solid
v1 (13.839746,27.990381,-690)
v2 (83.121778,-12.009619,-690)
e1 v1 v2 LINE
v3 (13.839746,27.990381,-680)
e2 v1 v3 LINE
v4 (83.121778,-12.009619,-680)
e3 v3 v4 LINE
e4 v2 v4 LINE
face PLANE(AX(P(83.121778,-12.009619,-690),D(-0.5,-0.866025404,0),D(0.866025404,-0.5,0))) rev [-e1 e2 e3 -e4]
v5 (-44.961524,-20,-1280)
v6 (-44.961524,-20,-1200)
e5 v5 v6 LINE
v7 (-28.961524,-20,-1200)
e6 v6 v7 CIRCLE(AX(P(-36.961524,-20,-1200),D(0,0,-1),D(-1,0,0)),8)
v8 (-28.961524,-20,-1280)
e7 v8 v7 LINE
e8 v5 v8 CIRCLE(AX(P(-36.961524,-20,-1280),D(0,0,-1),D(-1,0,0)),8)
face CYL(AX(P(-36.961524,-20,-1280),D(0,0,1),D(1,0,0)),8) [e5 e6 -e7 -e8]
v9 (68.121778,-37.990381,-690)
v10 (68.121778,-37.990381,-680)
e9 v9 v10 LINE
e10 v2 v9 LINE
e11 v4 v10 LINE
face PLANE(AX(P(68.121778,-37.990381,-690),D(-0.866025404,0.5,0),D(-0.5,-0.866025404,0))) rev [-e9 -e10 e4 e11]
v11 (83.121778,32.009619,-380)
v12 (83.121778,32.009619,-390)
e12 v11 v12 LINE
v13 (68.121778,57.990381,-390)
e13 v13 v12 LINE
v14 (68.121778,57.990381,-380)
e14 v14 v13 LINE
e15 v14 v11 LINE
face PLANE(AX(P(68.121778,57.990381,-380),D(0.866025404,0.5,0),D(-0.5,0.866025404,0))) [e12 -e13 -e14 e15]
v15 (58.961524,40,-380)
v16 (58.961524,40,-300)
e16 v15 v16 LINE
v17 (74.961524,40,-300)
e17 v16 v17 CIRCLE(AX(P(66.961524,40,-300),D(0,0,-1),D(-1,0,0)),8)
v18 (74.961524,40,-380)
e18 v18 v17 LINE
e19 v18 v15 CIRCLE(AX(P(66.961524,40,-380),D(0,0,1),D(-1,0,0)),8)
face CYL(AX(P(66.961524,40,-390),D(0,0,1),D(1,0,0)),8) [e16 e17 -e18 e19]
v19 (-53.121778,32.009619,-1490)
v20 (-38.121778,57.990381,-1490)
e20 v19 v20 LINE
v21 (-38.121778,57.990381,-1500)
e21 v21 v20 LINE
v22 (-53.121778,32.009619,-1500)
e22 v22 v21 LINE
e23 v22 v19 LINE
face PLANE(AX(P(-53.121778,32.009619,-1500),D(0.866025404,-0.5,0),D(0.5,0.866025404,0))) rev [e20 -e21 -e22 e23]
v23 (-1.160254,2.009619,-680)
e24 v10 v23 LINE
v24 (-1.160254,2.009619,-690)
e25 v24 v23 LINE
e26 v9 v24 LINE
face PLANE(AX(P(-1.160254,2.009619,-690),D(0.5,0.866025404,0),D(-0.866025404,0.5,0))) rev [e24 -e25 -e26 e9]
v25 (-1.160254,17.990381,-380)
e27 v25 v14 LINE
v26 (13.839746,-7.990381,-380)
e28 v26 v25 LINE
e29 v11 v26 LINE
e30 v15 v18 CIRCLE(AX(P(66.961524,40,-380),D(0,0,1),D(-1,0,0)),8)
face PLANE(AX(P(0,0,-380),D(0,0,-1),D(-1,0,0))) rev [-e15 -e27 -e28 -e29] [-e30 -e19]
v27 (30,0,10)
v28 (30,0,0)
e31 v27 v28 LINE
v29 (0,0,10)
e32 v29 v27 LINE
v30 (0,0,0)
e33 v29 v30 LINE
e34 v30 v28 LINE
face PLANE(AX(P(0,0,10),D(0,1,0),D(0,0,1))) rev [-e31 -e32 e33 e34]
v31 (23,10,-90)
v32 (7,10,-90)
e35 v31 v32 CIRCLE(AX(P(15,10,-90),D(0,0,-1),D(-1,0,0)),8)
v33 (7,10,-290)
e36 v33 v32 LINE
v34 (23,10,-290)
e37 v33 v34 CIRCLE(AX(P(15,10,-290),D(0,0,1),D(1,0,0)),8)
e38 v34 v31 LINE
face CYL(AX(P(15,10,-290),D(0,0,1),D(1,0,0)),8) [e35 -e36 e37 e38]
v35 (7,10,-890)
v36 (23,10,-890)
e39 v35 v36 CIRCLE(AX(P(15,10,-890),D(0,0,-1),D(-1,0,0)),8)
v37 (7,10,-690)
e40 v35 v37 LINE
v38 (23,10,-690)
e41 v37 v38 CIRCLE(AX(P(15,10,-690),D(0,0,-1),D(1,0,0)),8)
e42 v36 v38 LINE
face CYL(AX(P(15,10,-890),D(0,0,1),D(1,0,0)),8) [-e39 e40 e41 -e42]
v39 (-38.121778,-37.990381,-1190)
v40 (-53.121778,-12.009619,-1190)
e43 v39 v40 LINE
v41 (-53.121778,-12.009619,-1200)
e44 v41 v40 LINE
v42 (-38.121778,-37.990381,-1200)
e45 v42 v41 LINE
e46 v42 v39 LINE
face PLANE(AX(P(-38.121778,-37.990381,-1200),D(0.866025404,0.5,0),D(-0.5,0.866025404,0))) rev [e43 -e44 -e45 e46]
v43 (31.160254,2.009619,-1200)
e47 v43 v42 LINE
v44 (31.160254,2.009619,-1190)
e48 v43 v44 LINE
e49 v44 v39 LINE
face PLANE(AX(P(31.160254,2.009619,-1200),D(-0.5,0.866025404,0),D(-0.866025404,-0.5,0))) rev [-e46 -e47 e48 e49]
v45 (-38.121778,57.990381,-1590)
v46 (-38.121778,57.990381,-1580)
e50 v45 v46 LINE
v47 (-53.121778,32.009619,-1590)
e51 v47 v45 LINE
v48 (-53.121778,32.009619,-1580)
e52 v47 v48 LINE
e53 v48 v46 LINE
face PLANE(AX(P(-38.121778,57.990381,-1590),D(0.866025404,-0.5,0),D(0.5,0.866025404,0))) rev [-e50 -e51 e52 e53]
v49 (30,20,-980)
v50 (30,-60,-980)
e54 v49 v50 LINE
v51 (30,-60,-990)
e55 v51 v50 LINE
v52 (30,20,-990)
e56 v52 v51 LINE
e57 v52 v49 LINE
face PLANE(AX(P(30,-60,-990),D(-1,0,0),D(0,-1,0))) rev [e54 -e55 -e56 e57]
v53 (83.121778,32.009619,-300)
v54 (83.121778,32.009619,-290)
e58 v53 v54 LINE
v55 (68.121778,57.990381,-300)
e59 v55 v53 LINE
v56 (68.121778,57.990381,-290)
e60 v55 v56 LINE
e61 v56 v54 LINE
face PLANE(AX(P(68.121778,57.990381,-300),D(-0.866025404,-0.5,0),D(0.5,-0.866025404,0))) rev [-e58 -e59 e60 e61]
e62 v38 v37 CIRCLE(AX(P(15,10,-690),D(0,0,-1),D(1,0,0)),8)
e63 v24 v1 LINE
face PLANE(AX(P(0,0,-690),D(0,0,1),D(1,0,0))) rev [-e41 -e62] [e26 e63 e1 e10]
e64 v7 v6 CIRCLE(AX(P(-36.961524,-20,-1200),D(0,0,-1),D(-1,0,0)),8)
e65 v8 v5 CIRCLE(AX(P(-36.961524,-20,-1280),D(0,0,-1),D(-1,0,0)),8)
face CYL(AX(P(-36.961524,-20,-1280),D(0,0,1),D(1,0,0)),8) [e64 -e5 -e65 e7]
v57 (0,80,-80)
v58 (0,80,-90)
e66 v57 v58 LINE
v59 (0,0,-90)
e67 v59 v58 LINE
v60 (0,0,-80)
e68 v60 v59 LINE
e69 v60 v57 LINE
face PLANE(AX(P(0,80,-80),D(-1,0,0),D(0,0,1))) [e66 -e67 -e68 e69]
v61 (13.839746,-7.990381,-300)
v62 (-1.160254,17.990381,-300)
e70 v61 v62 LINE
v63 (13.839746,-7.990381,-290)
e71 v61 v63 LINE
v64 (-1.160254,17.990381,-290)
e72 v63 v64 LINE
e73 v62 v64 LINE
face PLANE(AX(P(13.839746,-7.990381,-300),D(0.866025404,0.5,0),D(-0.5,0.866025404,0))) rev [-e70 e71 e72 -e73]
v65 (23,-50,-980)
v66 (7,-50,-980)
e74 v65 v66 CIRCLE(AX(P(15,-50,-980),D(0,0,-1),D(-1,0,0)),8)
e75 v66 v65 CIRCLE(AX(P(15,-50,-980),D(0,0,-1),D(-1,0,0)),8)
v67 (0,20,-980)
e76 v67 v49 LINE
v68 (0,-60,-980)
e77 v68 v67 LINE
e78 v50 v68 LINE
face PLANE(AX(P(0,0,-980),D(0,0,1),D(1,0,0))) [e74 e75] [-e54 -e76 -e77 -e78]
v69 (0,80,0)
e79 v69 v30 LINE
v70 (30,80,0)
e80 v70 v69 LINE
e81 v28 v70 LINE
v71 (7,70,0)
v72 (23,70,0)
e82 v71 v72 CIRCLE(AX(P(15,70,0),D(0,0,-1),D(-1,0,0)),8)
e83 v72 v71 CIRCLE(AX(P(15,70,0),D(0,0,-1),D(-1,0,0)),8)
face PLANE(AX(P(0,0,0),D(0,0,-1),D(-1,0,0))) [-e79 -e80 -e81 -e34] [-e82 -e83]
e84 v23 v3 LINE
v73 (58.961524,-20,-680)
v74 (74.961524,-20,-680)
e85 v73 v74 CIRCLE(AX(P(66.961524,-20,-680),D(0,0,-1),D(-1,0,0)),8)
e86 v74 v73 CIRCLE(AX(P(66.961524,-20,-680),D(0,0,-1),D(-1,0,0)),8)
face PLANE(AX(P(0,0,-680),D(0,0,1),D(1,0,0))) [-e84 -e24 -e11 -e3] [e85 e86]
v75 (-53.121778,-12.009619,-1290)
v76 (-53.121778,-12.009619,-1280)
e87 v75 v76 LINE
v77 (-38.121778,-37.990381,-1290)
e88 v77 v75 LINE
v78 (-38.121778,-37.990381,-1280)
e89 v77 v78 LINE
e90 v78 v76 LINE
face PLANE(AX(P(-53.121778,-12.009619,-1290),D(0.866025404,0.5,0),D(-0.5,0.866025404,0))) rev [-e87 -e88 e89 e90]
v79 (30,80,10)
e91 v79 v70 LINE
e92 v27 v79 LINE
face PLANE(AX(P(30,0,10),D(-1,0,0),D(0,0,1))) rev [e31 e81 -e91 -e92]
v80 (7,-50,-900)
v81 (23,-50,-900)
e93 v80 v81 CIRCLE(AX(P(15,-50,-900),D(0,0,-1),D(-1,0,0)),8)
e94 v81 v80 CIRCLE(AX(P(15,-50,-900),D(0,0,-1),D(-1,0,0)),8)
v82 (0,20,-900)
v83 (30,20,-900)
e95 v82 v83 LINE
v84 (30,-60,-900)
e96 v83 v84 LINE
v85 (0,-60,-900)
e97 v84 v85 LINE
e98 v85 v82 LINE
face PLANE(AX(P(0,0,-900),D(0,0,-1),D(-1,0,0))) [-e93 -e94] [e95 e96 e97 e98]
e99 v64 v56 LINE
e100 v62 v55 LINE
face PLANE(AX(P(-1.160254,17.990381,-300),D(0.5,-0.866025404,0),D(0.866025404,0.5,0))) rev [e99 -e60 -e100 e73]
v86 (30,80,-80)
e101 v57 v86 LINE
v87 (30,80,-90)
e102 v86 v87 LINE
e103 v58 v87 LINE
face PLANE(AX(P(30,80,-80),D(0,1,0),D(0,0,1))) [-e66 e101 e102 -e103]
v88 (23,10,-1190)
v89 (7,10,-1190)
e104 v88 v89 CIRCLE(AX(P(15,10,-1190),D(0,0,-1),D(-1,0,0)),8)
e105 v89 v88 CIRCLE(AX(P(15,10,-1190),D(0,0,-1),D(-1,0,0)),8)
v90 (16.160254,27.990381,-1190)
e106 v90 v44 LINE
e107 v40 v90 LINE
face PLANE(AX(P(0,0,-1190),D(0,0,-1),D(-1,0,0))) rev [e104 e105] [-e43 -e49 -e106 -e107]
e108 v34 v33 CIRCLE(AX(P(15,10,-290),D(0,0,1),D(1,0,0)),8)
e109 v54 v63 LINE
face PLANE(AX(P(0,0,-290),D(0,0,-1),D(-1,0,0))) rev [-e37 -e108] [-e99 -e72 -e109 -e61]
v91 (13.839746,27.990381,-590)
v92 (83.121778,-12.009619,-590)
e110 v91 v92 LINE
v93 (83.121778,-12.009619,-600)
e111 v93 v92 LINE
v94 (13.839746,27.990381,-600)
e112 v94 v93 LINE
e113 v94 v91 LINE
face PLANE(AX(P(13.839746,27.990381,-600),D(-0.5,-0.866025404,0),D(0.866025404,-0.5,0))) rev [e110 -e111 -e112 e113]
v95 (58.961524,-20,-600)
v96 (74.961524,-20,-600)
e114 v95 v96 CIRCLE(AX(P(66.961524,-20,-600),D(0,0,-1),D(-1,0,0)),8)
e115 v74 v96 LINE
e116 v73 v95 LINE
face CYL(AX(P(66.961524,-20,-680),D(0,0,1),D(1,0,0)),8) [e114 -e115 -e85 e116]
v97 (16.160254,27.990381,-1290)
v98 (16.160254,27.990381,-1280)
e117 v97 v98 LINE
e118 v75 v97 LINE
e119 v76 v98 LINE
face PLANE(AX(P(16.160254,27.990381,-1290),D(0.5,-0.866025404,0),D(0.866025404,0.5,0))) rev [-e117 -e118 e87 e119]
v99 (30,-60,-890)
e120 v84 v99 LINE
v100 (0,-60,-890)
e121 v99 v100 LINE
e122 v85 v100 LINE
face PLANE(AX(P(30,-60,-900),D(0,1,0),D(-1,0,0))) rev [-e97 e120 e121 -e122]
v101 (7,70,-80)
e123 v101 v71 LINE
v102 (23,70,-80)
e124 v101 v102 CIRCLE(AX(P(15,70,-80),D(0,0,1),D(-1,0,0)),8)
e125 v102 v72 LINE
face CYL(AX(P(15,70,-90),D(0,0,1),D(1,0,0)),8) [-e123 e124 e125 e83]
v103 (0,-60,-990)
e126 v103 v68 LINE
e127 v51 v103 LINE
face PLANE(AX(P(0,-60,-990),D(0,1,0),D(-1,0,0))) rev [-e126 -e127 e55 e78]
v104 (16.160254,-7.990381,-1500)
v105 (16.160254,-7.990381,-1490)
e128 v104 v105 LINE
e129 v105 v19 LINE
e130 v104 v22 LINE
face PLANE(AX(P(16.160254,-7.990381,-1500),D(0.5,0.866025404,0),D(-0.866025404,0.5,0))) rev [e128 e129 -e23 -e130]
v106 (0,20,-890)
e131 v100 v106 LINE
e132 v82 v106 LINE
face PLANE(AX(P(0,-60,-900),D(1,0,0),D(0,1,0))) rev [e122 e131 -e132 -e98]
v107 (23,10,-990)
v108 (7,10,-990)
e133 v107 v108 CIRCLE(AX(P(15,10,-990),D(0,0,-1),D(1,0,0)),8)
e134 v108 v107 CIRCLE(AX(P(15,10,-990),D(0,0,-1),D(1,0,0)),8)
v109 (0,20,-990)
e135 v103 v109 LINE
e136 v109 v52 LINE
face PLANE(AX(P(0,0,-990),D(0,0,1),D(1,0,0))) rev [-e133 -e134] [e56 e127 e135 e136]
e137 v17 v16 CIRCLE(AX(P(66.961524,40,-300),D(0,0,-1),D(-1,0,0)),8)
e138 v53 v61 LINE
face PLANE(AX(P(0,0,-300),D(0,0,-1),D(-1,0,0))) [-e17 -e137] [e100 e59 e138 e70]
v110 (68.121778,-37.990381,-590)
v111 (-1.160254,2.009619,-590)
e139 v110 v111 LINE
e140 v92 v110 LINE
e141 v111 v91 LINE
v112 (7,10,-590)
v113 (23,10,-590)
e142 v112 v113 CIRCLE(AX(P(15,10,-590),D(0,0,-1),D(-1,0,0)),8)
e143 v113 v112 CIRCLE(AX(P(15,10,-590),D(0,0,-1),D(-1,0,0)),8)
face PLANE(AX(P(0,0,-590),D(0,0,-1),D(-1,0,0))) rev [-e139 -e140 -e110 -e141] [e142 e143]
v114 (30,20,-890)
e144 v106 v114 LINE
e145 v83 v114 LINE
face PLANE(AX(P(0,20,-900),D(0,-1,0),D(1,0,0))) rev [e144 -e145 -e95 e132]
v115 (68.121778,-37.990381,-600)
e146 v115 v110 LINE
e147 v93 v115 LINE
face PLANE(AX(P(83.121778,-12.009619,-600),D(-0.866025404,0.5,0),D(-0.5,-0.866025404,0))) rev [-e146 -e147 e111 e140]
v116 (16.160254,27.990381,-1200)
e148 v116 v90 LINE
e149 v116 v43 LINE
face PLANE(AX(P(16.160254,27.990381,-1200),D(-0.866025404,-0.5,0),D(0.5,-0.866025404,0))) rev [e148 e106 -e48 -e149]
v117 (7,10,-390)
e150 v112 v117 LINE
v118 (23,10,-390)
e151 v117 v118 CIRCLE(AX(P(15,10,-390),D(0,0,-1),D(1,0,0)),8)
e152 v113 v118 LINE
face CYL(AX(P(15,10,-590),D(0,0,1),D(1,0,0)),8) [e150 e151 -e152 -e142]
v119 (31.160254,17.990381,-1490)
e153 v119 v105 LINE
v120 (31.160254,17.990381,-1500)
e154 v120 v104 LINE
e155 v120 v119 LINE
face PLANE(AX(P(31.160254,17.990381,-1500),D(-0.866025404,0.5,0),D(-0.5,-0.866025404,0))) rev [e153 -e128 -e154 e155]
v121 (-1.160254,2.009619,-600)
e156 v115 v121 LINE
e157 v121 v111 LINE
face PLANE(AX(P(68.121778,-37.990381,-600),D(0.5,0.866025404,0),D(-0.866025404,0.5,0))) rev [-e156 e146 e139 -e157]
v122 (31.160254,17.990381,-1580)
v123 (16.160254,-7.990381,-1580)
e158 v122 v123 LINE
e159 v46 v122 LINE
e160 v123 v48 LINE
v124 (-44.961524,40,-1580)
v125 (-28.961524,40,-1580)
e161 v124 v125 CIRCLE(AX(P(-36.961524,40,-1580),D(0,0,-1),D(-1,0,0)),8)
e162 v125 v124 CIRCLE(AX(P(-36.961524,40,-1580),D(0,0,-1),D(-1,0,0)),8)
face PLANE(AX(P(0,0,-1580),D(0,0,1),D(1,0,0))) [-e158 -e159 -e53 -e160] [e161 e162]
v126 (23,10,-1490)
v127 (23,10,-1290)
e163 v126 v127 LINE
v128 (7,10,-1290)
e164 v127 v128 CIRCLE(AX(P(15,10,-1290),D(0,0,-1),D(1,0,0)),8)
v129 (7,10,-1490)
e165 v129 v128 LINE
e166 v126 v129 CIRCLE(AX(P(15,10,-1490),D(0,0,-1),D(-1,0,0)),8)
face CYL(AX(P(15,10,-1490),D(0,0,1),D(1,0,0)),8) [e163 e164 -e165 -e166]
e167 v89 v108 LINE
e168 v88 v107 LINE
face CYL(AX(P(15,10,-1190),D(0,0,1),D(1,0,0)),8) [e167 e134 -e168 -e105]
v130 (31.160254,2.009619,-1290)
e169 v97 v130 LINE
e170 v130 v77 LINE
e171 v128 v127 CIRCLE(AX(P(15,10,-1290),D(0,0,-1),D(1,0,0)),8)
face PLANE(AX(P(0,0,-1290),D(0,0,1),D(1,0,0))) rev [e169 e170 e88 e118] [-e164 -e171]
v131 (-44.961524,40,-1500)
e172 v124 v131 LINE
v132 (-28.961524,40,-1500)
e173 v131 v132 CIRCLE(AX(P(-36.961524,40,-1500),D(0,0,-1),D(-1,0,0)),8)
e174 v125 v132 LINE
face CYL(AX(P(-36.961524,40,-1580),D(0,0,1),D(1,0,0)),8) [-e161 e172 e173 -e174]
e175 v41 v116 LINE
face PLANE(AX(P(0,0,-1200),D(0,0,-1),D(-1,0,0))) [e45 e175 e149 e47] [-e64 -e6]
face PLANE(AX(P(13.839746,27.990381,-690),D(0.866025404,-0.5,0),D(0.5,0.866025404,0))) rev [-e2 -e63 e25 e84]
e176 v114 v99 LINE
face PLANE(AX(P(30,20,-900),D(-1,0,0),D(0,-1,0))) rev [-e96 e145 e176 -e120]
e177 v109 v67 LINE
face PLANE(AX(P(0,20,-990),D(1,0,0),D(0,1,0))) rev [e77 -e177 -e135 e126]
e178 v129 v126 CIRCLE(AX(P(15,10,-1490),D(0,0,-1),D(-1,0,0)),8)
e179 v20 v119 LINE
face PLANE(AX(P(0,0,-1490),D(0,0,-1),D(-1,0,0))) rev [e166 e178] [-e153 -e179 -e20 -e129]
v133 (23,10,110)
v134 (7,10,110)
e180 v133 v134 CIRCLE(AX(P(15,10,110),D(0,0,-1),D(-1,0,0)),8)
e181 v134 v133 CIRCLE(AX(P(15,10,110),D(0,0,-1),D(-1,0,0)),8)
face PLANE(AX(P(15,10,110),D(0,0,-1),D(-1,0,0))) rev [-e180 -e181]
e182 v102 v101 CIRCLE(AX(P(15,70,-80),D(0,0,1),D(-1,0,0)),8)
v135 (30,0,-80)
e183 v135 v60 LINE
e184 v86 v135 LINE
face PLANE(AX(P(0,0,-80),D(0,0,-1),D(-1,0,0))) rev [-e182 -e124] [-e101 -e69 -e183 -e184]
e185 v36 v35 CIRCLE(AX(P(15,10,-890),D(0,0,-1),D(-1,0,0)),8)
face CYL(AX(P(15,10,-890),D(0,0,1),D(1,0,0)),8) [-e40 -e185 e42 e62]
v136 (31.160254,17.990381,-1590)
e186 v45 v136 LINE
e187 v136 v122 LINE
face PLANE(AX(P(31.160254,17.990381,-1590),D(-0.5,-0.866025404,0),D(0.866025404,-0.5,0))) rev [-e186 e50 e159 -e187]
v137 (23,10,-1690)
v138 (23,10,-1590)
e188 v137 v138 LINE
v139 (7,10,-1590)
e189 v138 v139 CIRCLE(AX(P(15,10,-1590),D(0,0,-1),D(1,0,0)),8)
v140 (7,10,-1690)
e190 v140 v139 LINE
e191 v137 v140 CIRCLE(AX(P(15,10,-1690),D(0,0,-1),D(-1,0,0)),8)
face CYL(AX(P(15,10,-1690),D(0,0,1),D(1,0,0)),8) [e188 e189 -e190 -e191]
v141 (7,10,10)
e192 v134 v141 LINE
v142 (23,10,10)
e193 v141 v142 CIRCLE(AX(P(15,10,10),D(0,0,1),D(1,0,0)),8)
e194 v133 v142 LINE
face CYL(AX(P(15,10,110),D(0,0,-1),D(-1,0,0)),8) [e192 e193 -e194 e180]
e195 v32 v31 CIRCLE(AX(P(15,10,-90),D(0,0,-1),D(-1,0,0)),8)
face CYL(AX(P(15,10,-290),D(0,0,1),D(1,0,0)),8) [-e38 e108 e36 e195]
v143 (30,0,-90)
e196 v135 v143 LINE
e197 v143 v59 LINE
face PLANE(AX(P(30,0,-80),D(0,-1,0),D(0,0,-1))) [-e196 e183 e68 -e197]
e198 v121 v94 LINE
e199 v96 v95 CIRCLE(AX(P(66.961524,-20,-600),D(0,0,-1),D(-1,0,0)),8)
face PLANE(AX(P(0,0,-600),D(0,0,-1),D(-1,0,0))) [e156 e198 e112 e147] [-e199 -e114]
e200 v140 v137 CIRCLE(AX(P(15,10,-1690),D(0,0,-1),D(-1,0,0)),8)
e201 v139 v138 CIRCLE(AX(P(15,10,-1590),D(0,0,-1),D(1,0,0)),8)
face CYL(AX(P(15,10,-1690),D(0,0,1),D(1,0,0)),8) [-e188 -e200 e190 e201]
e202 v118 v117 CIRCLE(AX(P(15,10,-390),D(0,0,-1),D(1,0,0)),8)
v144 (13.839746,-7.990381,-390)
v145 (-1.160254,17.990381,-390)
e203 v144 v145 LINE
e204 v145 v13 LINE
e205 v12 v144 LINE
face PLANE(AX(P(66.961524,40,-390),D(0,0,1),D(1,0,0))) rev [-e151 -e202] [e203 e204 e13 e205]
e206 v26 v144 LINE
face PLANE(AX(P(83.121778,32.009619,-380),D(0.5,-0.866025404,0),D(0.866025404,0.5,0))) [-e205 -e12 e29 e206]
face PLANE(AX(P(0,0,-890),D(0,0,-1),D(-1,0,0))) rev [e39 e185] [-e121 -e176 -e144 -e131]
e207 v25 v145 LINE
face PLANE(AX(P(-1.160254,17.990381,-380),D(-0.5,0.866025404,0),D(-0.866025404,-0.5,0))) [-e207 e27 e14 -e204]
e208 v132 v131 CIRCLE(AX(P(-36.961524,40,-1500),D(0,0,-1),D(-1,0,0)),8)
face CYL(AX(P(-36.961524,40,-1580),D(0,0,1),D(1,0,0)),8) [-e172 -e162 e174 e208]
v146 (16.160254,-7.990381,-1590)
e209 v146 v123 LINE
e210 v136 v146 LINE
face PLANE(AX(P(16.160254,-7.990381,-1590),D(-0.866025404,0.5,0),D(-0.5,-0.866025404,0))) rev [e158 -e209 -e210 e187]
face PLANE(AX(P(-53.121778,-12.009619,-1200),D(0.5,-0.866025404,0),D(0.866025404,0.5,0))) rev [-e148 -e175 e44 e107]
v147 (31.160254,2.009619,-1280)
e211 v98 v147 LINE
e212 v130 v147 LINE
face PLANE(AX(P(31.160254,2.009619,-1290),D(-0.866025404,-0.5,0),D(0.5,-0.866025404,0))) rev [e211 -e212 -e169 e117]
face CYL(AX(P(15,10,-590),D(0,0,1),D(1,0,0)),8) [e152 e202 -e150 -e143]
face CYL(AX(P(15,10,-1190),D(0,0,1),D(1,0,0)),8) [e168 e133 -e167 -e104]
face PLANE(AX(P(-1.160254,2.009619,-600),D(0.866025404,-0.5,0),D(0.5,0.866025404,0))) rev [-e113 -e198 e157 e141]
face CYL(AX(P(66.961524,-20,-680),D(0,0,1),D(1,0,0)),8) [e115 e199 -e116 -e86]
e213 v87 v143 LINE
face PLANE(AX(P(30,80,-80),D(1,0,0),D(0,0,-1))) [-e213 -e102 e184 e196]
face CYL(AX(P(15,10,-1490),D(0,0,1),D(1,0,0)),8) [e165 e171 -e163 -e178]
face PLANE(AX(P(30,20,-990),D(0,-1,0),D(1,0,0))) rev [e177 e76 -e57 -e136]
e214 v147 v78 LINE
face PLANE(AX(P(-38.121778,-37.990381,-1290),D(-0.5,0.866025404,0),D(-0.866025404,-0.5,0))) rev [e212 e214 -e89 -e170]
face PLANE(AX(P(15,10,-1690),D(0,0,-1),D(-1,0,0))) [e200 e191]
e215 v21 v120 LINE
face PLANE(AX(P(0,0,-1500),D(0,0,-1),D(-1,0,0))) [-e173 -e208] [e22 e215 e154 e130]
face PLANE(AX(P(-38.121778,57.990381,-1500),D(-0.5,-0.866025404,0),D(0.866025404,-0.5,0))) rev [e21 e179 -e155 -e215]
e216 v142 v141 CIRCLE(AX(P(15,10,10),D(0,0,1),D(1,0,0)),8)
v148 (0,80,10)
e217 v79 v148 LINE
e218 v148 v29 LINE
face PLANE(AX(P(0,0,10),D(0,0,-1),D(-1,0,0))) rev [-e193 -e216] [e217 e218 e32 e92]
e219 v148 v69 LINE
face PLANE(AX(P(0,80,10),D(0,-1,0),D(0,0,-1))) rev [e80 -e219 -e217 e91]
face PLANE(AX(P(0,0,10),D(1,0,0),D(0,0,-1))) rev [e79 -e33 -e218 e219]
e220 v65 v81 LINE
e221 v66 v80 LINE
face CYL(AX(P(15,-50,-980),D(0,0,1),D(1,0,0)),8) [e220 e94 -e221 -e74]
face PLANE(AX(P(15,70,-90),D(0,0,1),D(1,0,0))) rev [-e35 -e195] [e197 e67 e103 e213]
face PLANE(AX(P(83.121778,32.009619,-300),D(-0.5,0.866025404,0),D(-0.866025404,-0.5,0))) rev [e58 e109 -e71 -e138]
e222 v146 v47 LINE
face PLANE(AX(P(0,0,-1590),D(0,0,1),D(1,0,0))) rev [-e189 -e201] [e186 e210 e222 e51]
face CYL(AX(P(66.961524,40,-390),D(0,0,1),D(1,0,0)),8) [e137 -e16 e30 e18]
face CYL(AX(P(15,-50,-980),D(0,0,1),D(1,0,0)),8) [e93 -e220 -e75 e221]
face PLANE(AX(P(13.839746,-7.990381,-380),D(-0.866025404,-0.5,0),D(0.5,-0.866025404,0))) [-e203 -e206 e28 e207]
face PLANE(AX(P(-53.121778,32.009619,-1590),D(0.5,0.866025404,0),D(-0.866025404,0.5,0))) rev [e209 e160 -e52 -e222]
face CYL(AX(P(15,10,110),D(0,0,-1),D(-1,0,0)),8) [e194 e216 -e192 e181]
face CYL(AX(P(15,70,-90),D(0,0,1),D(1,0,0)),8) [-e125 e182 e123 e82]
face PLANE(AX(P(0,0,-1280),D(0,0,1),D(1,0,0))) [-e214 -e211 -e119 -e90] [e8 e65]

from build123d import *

# Parameters (mm, degrees)
SKETCH1_W            = 30
SKETCH1_H            = 80
SKETCH1_R            = 8
BOSS_EXTRUDE1_DEPTH  = 10
BOSS_EXTRUDE2_START  = -100
SKETCH2_R            = 8
BOSS_EXTRUDE2_DEPTH  = 100
SKETCH3_W            = 30
SKETCH3_H            = 80
SKETCH3_R            = 8
BOSS_EXTRUDE3_DEPTH  = 10
BOSS_EXTRUDE4_START  = -210
SKETCH4_R            = 8
BOSS_EXTRUDE4_DEPTH  = 210
SKETCH5_R            = 8
BOSS_EXTRUDE5_DEPTH  = 10
SKETCH6_R            = 8
BOSS_EXTRUDE6_DEPTH  = 100
BOSS_EXTRUDE7_DEPTH  = 10
BOSS_EXTRUDE8_START  = 200
SKETCH8_R            = 8
BOSS_EXTRUDE8_DEPTH  = 200
BOSS_EXTRUDE9_DEPTH  = 10
SKETCH10_R           = 8
BOSS_EXTRUDE10_DEPTH = 80
BOSS_EXTRUDE11_DEPTH = 10
BOSS_EXTRUDE12_START = 200
SKETCH12_R           = 8
BOSS_EXTRUDE12_DEPTH = 200
SKETCH13_W           = 30
SKETCH13_H           = 80
BOSS_EXTRUDE13_DEPTH = 10
SKETCH14_R           = 8
BOSS_EXTRUDE14_DEPTH = 80
SKETCH15_W           = 30
SKETCH15_H           = 80
BOSS_EXTRUDE15_DEPTH = 10
BOSS_EXTRUDE16_START = 200
SKETCH16_R           = 8
BOSS_EXTRUDE16_DEPTH = 200
BOSS_EXTRUDE17_DEPTH = 10
SKETCH18_R           = 8
BOSS_EXTRUDE18_DEPTH = 80
BOSS_EXTRUDE19_DEPTH = 10
BOSS_EXTRUDE20_START = 200
SKETCH20_R           = 8
BOSS_EXTRUDE20_DEPTH = 200
BOSS_EXTRUDE21_DEPTH = 10
SKETCH22_R           = 8
BOSS_EXTRUDE22_DEPTH = 80
BOSS_EXTRUDE23_DEPTH = 10
BOSS_EXTRUDE24_START = 100
SKETCH24_R           = 8
BOSS_EXTRUDE24_DEPTH = 100
SKETCH25_R           = 8
BOSS_EXTRUDE25_DEPTH = 110


with BuildPart() as part:
    # Sketch1 → Boss-Extrude1 (new body)
    with BuildSketch(Plane.XY):
        with Locations((15, 40)):
            Rectangle(SKETCH1_W, SKETCH1_H)
        with Locations((15, 70)):
            Circle(SKETCH1_R, mode=Mode.SUBTRACT)
        with Locations((15, 10)):
            Circle(SKETCH1_R, mode=Mode.SUBTRACT)
    extrude(amount=BOSS_EXTRUDE1_DEPTH)

    # Sketch2 → Boss-Extrude2 (add)
    with BuildSketch(Plane.XY.offset(10).offset(BOSS_EXTRUDE2_START)):
        with Locations((15, 70)):
            Circle(SKETCH2_R)
    extrude(amount=BOSS_EXTRUDE2_DEPTH)

    # Sketch3 → Boss-Extrude3 (add)
    with BuildSketch(Plane(origin=(0, 0, -90), x_dir=(-1, 0, 0), z_dir=(0, 0, -1))):
        with Locations((-15, 40)):
            Rectangle(SKETCH3_W, SKETCH3_H)
        with Locations(Location((-15, 10, 0), (0, 0, 180))):
            Circle(SKETCH3_R, mode=Mode.SUBTRACT)
    extrude(amount=-BOSS_EXTRUDE3_DEPTH)

    # Sketch4 → Boss-Extrude4 (add)
    with BuildSketch(Plane.XY.offset(-80).offset(BOSS_EXTRUDE4_START)):
        with Locations((15, 10)):
            Circle(SKETCH4_R)
    extrude(amount=BOSS_EXTRUDE4_DEPTH)

    # Sketch5 → Boss-Extrude5 (add)
    with BuildSketch(Plane(origin=(0, 0, -290), x_dir=(-1, 0, 0), z_dir=(0, 0, -1))):
        Polygon((-83.121778265, 32.009618943), (-13.839745962, -7.990381057), (1.160254038, 17.990381057), (-68.121778265, 57.990381057), align=None)
        with Locations((-66.961524227, 40)):
            Circle(SKETCH5_R, mode=Mode.SUBTRACT)
    extrude(amount=BOSS_EXTRUDE5_DEPTH)

    # Sketch6 → Boss-Extrude6 (add)
    with BuildSketch(Plane.XY.offset(-290)):
        with Locations((66.961524227, 40)):
            Circle(SKETCH6_R)
    extrude(amount=-BOSS_EXTRUDE6_DEPTH)

    # Sketch7 → Boss-Extrude7 (add)
    with BuildSketch(Plane(origin=(0, 0, -390), x_dir=(-1, 0, 0), z_dir=(0, 0, -1))):
        Polygon((-83.121778265, 32.009618943), (-13.839745962, -7.990381057), (1.160254038, 17.990381057), (-68.121778265, 57.990381057), align=None)
    extrude(amount=-BOSS_EXTRUDE7_DEPTH)

    # Sketch8 → Boss-Extrude8 (add)
    with BuildSketch(Plane(origin=(0, 0, -390), x_dir=(-1, 0, 0), z_dir=(0, 0, -1)).offset(BOSS_EXTRUDE8_START)):
        with Locations(Location((-15, 10, 0), (0, 0, 180))):
            Circle(SKETCH8_R)
    extrude(amount=-BOSS_EXTRUDE8_DEPTH)

    # Sketch9 → Boss-Extrude9 (add)
    with BuildSketch(Plane(origin=(0, 0, -590), x_dir=(-1, 0, 0), z_dir=(0, 0, -1))):
        Polygon((-68.121778265, -37.990381057), (1.160254038, 2.009618943), (-13.839745962, 27.990381057), (-83.121778265, -12.009618943), align=None)
    extrude(amount=BOSS_EXTRUDE9_DEPTH)

    # Sketch10 → Boss-Extrude10 (add)
    with BuildSketch(Plane(origin=(0, 0, -600), x_dir=(-1, 0, 0), z_dir=(0, 0, -1))):
        with Locations((-66.961524227, -20)):
            Circle(SKETCH10_R)
    extrude(amount=BOSS_EXTRUDE10_DEPTH)

    # Sketch11 → Boss-Extrude11 (add)
    with BuildSketch(Plane(origin=(0, 0, -680), x_dir=(-1, 0, 0), z_dir=(0, 0, -1))):
        Polygon((-68.121778265, -37.990381057), (-83.121778265, -12.009618943), (-13.839745962, 27.990381057), (1.160254038, 2.009618943), align=None)
    extrude(amount=BOSS_EXTRUDE11_DEPTH)

    # Sketch12 → Boss-Extrude12 (add)
    with BuildSketch(Plane(origin=(0, 0, -690), x_dir=(-1, 0, 0), z_dir=(0, 0, -1)).offset(BOSS_EXTRUDE12_START)):
        with Locations(Location((-15, 10, 0), (0, 0, 180))):
            Circle(SKETCH12_R)
    extrude(amount=-BOSS_EXTRUDE12_DEPTH)

    # Sketch13 → Boss-Extrude13 (add)
    with BuildSketch(Plane(origin=(0, 0, -890), x_dir=(-1, 0, 0), z_dir=(0, 0, -1))):
        with Locations((-15, -20)):
            Rectangle(SKETCH13_W, SKETCH13_H)
    extrude(amount=BOSS_EXTRUDE13_DEPTH)

    # Sketch14 → Boss-Extrude14 (add)
    with BuildSketch(Plane(origin=(0, 0, -900), x_dir=(-1, 0, 0), z_dir=(0, 0, -1))):
        with Locations((-15, -50)):
            Circle(SKETCH14_R)
    extrude(amount=BOSS_EXTRUDE14_DEPTH)

    # Sketch15 → Boss-Extrude15 (add)
    with BuildSketch(Plane(origin=(0, 0, -980), x_dir=(-1, 0, 0), z_dir=(0, 0, -1))):
        with Locations((-15, -20)):
            Rectangle(SKETCH15_W, SKETCH15_H)
    extrude(amount=BOSS_EXTRUDE15_DEPTH)

    # Sketch16 → Boss-Extrude16 (add)
    with BuildSketch(Plane(origin=(0, 0, -990), x_dir=(-1, 0, 0), z_dir=(0, 0, -1)).offset(BOSS_EXTRUDE16_START)):
        with Locations(Location((-15, 10, 0), (0, 0, 180))):
            Circle(SKETCH16_R)
    extrude(amount=-BOSS_EXTRUDE16_DEPTH)

    # Sketch17 → Boss-Extrude17 (add)
    with BuildSketch(Plane(origin=(0, 0, -1190), x_dir=(-1, 0, 0), z_dir=(0, 0, -1))):
        Polygon((53.121778265, -12.009618943), (-16.160254038, 27.990381057), (-31.160254038, 2.009618943), (38.121778265, -37.990381057), align=None)
    extrude(amount=BOSS_EXTRUDE17_DEPTH)

    # Sketch18 → Boss-Extrude18 (add)
    with BuildSketch(Plane(origin=(0, 0, -1200), x_dir=(-1, 0, 0), z_dir=(0, 0, -1))):
        with Locations((36.961524227, -20)):
            Circle(SKETCH18_R)
    extrude(amount=BOSS_EXTRUDE18_DEPTH)

    # Sketch19 → Boss-Extrude19 (add)
    with BuildSketch(Plane(origin=(0, 0, -1280), x_dir=(-1, 0, 0), z_dir=(0, 0, -1))):
        Polygon((53.121778265, -12.009618943), (38.121778265, -37.990381057), (-31.160254038, 2.009618943), (-16.160254038, 27.990381057), align=None)
    extrude(amount=BOSS_EXTRUDE19_DEPTH)

    # Sketch20 → Boss-Extrude20 (add)
    with BuildSketch(Plane(origin=(0, 0, -1290), x_dir=(-1, 0, 0), z_dir=(0, 0, -1)).offset(BOSS_EXTRUDE20_START)):
        with Locations(Location((-15, 10, 0), (0, 0, 180))):
            Circle(SKETCH20_R)
    extrude(amount=-BOSS_EXTRUDE20_DEPTH)

    # Sketch21 → Boss-Extrude21 (add)
    with BuildSketch(Plane(origin=(0, 0, -1490), x_dir=(-1, 0, 0), z_dir=(0, 0, -1))):
        Polygon((38.121778265, 57.990381057), (-31.160254038, 17.990381057), (-16.160254038, -7.990381057), (53.121778265, 32.009618943), align=None)
    extrude(amount=BOSS_EXTRUDE21_DEPTH)

    # Sketch22 → Boss-Extrude22 (add)
    with BuildSketch(Plane(origin=(0, 0, -1500), x_dir=(-1, 0, 0), z_dir=(0, 0, -1))):
        with Locations((36.961524227, 40)):
            Circle(SKETCH22_R)
    extrude(amount=BOSS_EXTRUDE22_DEPTH)

    # Sketch23 → Boss-Extrude23 (add)
    with BuildSketch(Plane(origin=(0, 0, -1580), x_dir=(-1, 0, 0), z_dir=(0, 0, -1))):
        Polygon((38.121778265, 57.990381057), (53.121778265, 32.009618943), (-16.160254038, -7.990381057), (-31.160254038, 17.990381057), align=None)
    extrude(amount=BOSS_EXTRUDE23_DEPTH)

    # Sketch24 → Boss-Extrude24 (add)
    with BuildSketch(Plane(origin=(0, 0, -1590), x_dir=(-1, 0, 0), z_dir=(0, 0, -1)).offset(BOSS_EXTRUDE24_START)):
        with Locations(Location((-15, 10, 0), (0, 0, 180))):
            Circle(SKETCH24_R)
    extrude(amount=-BOSS_EXTRUDE24_DEPTH)

    # Sketch25 → Boss-Extrude25 (add)
    with BuildSketch(Plane(origin=(0, 0, 0), x_dir=(-1, 0, 0), z_dir=(0, 0, -1))):
        with Locations(Location((-15, 10, 0), (0, 0, 180))):
            Circle(SKETCH25_R)
    extrude(amount=-BOSS_EXTRUDE25_DEPTH)


solid = part.part
